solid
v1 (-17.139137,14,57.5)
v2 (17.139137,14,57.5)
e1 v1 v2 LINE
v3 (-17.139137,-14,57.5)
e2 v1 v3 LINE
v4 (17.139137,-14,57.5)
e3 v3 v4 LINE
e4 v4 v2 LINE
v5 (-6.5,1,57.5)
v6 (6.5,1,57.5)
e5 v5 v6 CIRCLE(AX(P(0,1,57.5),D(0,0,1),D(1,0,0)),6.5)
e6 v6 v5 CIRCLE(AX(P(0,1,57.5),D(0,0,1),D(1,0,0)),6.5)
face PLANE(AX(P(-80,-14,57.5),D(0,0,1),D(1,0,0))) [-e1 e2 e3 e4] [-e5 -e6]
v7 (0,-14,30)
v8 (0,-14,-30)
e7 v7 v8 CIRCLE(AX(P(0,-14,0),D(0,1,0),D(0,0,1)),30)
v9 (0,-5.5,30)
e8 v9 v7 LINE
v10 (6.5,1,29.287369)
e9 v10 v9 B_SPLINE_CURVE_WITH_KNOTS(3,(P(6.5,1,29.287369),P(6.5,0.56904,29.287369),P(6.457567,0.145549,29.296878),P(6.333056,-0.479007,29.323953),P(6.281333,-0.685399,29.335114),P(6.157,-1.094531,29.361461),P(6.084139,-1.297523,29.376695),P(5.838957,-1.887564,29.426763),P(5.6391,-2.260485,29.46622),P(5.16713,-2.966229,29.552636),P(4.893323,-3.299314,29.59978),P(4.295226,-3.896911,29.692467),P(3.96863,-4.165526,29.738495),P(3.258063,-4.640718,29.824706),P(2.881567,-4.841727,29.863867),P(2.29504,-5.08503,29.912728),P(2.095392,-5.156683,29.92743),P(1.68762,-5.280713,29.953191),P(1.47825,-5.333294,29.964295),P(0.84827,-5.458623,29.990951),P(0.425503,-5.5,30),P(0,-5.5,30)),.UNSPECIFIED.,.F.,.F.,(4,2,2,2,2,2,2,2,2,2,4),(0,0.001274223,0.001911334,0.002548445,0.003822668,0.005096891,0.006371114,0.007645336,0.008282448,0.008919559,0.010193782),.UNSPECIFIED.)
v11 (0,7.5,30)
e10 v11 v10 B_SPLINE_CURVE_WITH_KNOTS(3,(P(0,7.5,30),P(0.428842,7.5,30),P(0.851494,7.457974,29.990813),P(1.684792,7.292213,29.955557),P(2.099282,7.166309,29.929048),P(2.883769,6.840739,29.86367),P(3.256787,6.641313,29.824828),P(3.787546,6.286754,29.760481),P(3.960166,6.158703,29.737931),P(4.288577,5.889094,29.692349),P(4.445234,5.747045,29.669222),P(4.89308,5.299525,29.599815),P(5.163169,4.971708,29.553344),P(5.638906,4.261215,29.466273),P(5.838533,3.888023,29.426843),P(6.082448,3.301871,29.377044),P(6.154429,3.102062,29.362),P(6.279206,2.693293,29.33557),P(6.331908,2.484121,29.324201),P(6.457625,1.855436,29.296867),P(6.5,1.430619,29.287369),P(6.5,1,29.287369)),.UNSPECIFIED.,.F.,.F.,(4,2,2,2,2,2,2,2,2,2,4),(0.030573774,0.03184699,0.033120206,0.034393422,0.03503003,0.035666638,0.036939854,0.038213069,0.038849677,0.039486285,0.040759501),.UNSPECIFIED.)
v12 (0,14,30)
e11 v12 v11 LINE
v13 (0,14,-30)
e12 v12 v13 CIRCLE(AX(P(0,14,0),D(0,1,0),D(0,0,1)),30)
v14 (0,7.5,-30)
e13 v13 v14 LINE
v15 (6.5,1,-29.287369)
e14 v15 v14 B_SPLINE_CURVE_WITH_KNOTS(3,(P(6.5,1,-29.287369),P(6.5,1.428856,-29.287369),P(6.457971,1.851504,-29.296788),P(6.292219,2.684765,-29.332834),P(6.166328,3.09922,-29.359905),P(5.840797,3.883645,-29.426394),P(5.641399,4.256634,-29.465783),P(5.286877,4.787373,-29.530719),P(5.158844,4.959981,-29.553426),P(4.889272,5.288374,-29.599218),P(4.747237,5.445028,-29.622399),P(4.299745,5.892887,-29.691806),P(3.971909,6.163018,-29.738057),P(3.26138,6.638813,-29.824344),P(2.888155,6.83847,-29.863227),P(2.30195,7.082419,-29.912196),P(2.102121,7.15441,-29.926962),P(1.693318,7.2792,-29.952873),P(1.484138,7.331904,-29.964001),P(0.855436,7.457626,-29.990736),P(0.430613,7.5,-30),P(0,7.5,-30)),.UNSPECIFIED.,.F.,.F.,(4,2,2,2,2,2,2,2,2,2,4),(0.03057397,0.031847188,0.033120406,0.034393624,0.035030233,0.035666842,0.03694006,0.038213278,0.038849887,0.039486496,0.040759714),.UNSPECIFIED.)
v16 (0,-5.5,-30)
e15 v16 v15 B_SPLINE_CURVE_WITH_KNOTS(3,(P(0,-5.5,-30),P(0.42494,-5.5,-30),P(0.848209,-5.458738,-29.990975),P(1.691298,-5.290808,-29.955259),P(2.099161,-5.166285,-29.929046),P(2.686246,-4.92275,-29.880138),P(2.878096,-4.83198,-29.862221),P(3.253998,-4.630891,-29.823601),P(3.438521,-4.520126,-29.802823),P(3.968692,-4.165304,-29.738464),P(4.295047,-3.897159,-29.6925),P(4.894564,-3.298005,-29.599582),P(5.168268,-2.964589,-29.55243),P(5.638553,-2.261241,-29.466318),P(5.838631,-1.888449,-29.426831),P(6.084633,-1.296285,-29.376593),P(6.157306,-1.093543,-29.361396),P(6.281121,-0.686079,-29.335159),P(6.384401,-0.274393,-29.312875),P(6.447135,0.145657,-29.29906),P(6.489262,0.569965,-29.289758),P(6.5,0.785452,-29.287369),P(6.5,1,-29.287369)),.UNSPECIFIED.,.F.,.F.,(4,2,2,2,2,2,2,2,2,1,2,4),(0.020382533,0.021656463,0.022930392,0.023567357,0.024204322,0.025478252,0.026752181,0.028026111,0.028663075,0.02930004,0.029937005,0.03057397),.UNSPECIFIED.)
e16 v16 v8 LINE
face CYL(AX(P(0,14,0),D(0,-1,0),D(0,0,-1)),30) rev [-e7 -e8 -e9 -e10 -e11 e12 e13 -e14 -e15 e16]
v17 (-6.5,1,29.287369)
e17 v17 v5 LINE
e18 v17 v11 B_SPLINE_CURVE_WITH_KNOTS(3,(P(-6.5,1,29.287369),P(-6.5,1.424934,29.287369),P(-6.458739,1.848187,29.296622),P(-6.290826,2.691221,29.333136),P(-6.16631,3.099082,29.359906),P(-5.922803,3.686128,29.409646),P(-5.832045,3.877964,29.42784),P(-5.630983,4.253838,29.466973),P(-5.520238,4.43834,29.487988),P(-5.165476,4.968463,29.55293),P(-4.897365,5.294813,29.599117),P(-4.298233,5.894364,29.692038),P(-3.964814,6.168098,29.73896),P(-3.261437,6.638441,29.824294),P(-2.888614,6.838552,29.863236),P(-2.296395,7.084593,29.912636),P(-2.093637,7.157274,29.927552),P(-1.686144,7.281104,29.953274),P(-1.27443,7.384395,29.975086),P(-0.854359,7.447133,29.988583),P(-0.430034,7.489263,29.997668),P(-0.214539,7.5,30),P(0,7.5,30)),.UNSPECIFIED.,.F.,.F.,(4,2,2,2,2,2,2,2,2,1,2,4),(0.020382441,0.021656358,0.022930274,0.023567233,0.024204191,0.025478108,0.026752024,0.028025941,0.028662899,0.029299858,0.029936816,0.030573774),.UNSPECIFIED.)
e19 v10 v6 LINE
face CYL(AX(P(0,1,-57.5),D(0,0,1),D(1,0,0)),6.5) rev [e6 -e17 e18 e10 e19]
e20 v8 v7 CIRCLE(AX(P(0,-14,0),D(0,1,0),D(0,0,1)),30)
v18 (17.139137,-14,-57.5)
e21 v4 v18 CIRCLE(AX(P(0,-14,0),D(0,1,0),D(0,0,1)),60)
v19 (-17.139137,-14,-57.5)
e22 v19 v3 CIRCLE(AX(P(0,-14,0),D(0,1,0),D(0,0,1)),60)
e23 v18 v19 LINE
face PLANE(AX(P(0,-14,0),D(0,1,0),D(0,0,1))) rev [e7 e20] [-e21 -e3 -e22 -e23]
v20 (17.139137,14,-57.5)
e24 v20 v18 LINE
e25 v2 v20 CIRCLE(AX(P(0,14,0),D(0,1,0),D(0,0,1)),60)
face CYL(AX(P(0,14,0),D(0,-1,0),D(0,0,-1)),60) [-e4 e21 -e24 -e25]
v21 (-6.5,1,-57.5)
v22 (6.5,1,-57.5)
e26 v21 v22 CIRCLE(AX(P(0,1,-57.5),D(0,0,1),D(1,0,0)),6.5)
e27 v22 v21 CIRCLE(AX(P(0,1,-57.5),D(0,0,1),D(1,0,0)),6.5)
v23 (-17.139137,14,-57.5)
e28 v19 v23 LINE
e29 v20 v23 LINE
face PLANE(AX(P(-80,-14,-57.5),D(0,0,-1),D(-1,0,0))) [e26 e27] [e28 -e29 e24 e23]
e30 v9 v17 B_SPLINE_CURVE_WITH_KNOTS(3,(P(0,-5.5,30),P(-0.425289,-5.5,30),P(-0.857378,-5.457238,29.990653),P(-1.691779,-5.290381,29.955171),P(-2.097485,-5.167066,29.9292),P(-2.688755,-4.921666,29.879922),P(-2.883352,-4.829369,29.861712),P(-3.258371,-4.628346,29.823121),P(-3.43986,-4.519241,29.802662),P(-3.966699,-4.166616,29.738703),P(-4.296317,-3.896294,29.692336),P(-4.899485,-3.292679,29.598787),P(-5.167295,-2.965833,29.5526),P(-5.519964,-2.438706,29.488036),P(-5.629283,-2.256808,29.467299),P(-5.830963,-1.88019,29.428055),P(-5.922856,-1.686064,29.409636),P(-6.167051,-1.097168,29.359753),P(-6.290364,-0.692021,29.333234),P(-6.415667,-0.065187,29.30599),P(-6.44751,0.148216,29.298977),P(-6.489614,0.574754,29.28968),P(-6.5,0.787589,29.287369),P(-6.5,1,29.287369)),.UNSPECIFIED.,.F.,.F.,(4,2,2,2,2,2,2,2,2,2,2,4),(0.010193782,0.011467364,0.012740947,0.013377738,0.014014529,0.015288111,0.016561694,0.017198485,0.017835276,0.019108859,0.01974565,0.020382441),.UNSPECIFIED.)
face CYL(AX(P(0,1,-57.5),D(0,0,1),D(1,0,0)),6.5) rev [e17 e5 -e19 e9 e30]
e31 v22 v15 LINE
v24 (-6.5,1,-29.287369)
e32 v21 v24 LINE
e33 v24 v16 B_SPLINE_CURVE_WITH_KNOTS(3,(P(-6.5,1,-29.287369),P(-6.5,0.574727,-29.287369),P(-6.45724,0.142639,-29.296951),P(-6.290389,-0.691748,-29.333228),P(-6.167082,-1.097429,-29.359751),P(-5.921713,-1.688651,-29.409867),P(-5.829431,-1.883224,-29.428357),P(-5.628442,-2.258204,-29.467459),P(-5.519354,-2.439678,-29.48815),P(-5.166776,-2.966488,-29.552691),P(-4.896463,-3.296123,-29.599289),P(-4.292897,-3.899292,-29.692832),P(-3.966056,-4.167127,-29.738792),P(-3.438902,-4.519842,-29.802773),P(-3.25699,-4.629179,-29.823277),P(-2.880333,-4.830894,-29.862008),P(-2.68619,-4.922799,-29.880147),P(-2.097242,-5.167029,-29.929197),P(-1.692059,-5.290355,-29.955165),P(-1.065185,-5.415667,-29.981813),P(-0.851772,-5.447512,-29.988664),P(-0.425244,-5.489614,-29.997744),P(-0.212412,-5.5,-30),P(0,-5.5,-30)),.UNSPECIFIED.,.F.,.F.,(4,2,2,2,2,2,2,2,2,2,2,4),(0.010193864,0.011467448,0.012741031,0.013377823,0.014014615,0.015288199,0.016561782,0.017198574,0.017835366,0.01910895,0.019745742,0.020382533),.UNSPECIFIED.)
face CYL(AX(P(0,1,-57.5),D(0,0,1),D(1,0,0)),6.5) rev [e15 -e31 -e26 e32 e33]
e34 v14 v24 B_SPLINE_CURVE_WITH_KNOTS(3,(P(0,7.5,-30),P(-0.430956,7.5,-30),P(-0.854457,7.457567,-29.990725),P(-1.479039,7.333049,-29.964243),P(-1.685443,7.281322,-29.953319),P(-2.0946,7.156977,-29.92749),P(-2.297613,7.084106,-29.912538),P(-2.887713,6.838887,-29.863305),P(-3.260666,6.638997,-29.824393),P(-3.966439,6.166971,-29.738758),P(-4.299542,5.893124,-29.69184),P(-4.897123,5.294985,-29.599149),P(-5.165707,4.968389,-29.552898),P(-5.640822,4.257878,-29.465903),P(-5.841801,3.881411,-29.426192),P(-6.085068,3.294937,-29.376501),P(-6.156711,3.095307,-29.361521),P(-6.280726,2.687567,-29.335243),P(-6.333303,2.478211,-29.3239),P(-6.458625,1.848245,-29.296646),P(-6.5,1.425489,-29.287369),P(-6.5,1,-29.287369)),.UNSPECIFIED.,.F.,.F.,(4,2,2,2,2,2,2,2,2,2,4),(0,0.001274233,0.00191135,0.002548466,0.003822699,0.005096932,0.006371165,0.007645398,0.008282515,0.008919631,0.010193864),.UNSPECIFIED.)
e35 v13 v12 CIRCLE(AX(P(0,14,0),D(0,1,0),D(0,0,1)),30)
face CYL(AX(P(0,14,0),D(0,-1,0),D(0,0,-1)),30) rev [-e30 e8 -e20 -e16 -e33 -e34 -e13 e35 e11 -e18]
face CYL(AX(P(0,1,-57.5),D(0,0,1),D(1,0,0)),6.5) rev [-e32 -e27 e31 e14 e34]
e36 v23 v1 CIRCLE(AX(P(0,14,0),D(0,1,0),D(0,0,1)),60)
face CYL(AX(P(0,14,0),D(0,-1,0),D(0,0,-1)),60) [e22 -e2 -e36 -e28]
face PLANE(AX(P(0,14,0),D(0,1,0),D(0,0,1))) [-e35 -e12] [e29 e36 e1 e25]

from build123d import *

# Parameters (mm, degrees)
SKETCH1_R               = 60
SKETCH1_R_2             = 30
BOSS_EXTRUDE1_DEPTH     = 14
CUT_EXTRUDE1_DEPTH      = 87
CUT_EXTRUDE1_DEPTH_BACK = 87
SKETCH2_OUTSIDE_W       = 156.4
SKETCH2_OUTSIDE_H       = 156.4
SKETCH2_OUTSIDE_W_2     = 160
SKETCH2_OUTSIDE_H_2     = 115
SKETCH3_R               = 6.5
CUT_EXTRUDE2_DEPTH      = 131.464554573


with BuildPart() as part:
    # Sketch1 → Boss-Extrude1 (new, symmetric)
    with BuildSketch(Plane(origin=(0, 0, 0), x_dir=(1, 0, 0), z_dir=(0, 1, 0))):
        with Locations(Location((0, 0, 0), (0, 0, 270))):
            Circle(SKETCH1_R)
        with Locations(Location((0, 0, 0), (0, 0, 270))):
            Circle(SKETCH1_R_2, mode=Mode.SUBTRACT)
    extrude(amount=BOSS_EXTRUDE1_DEPTH, both=True)

    # Sketch2 outside → Cut-Extrude1 (cut, two sides: drawn at the far end of the back side and taken through both)
    with BuildSketch(Plane(origin=(0, 0, 0), x_dir=(1, 0, 0), z_dir=(0, 1, 0)).offset(-CUT_EXTRUDE1_DEPTH_BACK)):
        Rectangle(SKETCH2_OUTSIDE_W, SKETCH2_OUTSIDE_H)
        Rectangle(SKETCH2_OUTSIDE_W_2, SKETCH2_OUTSIDE_H_2, mode=Mode.SUBTRACT)
    extrude(amount=CUT_EXTRUDE1_DEPTH + CUT_EXTRUDE1_DEPTH_BACK, mode=Mode.SUBTRACT)

    # Sketch3 → Cut-Extrude2 (cut, through all)
    with BuildSketch(Plane.XY.offset(57.5)):
        with Locations((0, 1)):
            Circle(SKETCH3_R)
    extrude(amount=-CUT_EXTRUDE2_DEPTH, mode=Mode.SUBTRACT)


solid = part.part
